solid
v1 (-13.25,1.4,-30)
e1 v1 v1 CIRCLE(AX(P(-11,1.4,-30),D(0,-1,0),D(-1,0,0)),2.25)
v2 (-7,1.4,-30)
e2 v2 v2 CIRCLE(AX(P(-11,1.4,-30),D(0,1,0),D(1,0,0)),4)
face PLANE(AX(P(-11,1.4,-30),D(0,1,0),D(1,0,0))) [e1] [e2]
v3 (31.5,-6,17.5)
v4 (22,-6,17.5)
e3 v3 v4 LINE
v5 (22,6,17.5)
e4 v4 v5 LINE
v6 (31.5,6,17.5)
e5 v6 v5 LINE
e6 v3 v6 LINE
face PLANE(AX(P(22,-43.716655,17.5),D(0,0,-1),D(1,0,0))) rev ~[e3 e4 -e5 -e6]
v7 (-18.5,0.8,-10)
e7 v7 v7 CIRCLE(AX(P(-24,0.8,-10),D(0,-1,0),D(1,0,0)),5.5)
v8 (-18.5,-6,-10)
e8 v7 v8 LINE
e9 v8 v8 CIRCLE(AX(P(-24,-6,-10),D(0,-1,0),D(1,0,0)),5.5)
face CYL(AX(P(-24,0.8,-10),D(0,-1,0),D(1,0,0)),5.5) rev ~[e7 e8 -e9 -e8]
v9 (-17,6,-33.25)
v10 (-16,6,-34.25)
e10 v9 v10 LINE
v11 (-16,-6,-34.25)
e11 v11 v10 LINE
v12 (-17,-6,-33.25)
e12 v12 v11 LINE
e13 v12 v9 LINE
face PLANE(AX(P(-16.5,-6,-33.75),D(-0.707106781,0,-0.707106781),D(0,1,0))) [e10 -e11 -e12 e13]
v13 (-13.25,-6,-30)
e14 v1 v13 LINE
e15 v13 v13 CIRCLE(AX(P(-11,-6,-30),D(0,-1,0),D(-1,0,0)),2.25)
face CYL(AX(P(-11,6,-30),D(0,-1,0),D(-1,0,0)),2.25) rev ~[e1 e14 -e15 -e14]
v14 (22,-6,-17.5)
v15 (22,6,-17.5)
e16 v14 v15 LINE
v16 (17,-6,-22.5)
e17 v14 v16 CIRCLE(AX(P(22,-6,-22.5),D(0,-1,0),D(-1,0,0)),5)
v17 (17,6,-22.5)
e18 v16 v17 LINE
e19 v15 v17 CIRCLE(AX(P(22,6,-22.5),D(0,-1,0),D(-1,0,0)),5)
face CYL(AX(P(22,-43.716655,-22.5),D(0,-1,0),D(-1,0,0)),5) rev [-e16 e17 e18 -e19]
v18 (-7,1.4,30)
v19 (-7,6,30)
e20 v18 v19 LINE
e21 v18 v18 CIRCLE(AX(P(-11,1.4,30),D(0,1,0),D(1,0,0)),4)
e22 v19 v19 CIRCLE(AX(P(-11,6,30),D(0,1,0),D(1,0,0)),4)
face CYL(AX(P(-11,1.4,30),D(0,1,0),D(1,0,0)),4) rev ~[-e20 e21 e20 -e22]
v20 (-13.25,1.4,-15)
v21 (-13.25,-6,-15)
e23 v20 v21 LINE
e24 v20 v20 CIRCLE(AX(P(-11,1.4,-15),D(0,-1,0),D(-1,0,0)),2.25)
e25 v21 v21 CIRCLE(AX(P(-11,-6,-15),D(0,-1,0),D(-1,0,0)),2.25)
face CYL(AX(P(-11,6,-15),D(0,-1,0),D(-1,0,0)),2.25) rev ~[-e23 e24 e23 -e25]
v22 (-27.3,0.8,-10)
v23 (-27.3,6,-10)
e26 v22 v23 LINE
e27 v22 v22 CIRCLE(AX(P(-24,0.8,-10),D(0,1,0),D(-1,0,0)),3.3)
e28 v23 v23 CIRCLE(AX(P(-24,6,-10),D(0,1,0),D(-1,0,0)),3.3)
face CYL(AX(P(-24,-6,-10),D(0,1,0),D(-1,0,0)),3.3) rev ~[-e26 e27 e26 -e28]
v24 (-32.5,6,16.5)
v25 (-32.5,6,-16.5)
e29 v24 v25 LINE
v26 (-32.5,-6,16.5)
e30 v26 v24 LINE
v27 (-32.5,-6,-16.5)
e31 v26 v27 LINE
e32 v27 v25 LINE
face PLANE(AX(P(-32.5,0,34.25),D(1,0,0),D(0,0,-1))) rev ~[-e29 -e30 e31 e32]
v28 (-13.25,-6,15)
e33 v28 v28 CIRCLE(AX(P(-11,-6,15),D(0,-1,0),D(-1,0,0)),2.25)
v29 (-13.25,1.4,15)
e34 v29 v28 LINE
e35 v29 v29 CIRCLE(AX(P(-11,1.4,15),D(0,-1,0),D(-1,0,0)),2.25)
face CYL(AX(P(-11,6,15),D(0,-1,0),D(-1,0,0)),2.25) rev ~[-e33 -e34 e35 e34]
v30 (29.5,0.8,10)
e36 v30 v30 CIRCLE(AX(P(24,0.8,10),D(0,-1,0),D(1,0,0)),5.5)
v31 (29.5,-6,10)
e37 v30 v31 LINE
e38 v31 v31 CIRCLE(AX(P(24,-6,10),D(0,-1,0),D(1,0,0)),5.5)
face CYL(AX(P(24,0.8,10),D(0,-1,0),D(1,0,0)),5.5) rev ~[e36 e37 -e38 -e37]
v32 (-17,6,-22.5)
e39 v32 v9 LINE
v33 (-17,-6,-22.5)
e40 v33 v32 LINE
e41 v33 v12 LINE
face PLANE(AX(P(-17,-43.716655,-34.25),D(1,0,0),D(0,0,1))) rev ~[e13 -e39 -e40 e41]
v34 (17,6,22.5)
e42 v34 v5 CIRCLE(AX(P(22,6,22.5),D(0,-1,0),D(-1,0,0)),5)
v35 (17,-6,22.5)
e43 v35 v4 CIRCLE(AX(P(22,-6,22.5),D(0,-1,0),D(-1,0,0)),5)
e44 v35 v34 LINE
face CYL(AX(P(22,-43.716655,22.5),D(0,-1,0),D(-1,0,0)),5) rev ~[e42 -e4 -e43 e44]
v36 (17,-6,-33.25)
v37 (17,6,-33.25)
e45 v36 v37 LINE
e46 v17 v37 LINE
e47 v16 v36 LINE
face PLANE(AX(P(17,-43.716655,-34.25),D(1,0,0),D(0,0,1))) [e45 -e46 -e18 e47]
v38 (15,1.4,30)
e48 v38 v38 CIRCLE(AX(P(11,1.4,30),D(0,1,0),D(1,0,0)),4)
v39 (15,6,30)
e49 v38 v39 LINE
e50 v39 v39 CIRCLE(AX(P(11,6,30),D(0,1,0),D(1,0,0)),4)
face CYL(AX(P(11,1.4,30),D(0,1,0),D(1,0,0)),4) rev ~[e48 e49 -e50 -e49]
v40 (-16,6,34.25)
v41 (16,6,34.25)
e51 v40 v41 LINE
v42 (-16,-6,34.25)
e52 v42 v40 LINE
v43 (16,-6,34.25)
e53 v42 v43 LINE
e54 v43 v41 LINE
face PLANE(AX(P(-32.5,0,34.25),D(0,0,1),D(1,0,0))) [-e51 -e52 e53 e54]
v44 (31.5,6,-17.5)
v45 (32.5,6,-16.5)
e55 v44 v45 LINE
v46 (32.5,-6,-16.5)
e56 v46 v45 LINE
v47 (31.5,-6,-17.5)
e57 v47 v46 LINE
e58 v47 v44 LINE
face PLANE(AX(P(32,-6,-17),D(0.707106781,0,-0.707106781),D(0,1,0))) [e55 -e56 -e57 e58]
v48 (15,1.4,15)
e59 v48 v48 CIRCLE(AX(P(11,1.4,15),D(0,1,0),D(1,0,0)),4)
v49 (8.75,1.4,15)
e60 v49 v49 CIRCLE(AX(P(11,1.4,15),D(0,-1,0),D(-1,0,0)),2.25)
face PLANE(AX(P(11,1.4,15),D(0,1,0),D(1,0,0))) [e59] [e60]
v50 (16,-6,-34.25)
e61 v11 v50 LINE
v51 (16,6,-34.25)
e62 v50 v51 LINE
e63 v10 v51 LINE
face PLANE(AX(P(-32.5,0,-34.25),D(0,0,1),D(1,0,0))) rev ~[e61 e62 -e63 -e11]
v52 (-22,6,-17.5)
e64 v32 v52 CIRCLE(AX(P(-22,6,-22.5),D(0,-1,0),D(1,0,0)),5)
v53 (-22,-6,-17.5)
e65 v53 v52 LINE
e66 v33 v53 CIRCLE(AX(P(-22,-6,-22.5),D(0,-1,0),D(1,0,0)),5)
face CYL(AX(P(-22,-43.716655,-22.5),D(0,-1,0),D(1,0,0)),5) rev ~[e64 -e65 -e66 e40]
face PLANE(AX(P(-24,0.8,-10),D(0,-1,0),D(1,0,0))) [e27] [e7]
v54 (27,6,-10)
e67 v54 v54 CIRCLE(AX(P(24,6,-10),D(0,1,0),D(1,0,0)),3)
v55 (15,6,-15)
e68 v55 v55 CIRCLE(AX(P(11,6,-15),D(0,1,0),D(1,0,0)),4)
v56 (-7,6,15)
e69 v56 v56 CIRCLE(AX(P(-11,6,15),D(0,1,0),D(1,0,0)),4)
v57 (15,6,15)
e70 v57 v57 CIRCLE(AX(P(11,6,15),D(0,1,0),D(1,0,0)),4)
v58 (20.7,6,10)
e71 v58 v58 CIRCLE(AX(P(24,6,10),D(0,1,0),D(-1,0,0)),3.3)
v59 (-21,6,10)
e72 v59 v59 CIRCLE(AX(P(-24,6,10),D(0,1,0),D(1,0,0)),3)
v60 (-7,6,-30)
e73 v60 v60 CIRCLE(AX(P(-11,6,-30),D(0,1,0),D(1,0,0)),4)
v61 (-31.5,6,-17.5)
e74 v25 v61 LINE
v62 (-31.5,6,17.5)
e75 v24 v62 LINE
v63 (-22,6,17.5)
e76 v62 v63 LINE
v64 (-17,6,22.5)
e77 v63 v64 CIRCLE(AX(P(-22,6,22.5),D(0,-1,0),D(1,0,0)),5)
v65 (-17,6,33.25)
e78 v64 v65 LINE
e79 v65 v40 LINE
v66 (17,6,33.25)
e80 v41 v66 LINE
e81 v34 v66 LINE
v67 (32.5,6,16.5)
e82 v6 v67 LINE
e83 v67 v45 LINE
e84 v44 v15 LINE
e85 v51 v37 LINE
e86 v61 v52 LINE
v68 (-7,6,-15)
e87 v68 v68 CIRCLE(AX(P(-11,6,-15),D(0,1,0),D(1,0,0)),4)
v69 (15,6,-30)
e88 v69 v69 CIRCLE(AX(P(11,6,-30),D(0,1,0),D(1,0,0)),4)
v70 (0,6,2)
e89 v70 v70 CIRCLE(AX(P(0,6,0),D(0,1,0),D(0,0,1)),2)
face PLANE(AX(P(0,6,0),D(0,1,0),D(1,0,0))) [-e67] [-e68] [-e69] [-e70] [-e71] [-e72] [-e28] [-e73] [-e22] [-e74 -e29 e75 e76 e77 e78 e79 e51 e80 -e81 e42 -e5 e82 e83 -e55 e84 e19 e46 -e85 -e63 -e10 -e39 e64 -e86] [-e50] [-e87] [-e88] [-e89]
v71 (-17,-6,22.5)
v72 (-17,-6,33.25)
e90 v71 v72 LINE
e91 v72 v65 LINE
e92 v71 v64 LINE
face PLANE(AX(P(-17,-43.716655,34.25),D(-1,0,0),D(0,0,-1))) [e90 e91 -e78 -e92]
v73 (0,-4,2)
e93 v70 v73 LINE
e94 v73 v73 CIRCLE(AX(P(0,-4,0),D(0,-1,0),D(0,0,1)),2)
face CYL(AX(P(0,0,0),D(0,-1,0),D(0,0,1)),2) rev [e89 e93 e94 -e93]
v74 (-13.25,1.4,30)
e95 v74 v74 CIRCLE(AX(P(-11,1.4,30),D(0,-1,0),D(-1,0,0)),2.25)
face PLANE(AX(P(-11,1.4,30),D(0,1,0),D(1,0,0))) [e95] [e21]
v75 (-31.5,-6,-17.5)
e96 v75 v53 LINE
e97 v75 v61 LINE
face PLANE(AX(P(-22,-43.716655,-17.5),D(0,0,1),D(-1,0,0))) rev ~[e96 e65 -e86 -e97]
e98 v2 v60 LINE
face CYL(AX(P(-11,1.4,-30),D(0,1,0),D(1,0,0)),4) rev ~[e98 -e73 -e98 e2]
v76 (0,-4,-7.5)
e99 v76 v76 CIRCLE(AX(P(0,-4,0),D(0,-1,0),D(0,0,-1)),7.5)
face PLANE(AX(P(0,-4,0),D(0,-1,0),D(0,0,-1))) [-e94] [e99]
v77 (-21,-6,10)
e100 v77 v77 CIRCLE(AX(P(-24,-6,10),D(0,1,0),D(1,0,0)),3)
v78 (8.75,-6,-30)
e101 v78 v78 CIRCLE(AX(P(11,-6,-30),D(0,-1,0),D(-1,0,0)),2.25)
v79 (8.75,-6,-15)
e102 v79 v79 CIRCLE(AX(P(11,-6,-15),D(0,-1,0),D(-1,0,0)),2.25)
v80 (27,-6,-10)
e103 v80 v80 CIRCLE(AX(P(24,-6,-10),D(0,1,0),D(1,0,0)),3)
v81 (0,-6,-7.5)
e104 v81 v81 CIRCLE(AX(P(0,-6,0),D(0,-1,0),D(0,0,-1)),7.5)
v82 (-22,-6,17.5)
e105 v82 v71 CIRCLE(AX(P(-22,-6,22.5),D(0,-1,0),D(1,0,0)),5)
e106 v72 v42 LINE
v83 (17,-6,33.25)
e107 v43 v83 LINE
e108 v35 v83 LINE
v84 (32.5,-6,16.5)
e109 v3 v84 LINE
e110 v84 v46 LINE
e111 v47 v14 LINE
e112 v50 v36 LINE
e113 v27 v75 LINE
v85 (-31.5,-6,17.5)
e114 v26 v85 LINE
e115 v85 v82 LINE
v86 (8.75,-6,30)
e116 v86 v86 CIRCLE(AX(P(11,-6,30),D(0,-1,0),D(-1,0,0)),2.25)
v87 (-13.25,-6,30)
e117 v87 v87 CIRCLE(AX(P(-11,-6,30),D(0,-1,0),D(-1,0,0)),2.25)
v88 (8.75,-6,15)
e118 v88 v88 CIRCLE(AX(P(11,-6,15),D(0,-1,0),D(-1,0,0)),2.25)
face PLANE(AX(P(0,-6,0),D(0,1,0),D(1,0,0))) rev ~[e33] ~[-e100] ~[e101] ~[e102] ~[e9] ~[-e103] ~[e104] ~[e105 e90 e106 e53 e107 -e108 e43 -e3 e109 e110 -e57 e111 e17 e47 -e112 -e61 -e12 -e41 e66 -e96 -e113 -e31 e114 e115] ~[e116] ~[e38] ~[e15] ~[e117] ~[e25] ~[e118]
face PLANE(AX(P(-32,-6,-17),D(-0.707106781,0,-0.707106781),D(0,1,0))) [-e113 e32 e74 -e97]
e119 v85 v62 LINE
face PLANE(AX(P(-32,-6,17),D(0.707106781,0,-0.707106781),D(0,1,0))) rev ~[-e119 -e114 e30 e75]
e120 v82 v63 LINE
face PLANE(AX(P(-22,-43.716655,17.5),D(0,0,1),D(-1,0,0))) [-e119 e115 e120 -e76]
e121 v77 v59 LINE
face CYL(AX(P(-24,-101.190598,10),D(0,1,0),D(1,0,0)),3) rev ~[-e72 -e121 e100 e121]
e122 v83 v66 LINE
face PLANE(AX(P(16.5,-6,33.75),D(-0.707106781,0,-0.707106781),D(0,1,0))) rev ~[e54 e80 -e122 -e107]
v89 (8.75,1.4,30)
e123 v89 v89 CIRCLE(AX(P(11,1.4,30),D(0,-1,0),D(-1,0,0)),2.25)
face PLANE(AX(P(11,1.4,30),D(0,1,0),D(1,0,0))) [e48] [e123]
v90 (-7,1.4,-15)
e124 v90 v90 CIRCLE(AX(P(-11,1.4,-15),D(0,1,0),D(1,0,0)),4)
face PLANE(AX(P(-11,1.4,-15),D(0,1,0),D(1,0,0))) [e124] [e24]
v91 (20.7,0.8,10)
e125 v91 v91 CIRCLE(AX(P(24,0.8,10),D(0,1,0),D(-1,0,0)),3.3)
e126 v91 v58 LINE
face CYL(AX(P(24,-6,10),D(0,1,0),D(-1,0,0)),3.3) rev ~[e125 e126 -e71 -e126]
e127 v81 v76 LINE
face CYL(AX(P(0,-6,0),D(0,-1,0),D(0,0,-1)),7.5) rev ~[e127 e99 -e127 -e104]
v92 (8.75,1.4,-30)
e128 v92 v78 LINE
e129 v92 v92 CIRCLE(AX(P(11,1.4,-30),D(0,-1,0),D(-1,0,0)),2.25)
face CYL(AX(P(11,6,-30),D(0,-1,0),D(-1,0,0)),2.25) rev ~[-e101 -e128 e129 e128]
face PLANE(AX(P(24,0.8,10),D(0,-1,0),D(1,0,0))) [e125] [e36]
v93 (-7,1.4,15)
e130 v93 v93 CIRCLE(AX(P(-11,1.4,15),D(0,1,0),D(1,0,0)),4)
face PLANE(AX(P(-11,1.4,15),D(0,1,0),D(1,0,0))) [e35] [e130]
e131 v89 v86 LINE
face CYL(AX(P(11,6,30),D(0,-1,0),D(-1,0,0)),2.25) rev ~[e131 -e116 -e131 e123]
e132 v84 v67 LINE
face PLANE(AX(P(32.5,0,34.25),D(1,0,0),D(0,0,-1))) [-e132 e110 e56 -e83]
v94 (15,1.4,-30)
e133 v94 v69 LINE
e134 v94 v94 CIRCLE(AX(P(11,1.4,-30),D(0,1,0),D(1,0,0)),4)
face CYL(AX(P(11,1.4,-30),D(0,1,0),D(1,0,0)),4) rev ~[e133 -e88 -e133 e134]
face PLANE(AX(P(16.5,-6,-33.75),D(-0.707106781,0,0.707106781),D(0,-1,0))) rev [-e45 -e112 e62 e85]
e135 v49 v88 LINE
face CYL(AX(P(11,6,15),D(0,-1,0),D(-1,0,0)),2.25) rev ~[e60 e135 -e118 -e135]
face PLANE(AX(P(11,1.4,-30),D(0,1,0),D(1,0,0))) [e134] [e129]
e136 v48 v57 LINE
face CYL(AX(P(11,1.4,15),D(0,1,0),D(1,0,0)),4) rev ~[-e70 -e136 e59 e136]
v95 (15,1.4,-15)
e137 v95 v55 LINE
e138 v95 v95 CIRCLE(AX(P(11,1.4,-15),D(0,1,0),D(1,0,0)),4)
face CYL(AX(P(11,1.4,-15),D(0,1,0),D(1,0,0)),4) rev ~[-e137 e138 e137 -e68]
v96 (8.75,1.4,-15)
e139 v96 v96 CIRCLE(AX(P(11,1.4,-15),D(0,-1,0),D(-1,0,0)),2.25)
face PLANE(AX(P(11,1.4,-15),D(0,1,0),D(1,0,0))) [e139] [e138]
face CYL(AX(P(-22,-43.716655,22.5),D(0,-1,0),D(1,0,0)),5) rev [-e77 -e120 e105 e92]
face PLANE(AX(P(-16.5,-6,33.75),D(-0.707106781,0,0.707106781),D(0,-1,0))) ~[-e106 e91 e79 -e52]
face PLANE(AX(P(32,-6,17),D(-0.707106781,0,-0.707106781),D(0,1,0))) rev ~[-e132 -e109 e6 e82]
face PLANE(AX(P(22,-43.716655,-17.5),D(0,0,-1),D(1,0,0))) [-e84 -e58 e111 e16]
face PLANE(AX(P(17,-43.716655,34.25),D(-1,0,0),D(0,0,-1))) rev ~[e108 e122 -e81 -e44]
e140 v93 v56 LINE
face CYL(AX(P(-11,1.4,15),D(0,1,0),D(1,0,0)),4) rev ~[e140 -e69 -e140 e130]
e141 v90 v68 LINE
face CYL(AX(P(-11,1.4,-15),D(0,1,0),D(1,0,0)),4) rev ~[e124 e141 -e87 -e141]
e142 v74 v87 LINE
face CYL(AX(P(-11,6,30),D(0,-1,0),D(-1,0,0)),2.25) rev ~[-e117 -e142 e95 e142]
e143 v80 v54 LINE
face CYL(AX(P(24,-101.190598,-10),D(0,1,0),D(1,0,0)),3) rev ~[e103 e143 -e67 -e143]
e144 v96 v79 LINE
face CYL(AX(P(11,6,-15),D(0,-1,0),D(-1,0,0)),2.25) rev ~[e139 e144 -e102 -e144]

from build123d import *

# Parameters (mm, degrees)
SKETCH_1_W                   = 65
SKETCH_1_H                   = 68.5
SKETCH_1_R                   = 2
EXTRUDE_1_DEPTH              = 6
HOLE_WIZARD_M6_1_D           = 6.6
HOLE_WIZARD_M6_1_CBORE_D     = 11
HOLE_WIZARD_M6_1_CBORE_DEPTH = 6.8
HOLE_WIZARD_M4_1_D           = 4.5
HOLE_WIZARD_M4_1_CBORE_D     = 8
HOLE_WIZARD_M4_1_CBORE_DEPTH = 4.6
CUT_EXTRUDE_1_DEPTH          = 49.716655263
CUT_EXTRUDE_1_DEPTH_BACK     = 49.716655263
F_6_0MM_1_D                  = 6
CHAMFER_1_SIZE               = 1
SKETCH_9_R                   = 7.5
CUT_EXTRUDE_2_DEPTH          = 2


with BuildPart() as part:
    # 草图1 → 凸台-拉伸1 (new, symmetric)
    with BuildSketch(Plane(origin=(0, 0, 0), x_dir=(1, 0, 0), z_dir=(0, 1, 0))):
        Rectangle(SKETCH_1_W, SKETCH_1_H)
        with Locations(Location((0, 0, 0), (0, 0, 270))):
            Circle(SKETCH_1_R, mode=Mode.SUBTRACT)
    extrude(amount=EXTRUDE_1_DEPTH, both=True)

    # M6 六角圆柱头螺钉的柱形沉头孔1 (through all)
    with Locations(Plane.XZ.offset(6)):
        with Locations((-24, -10), (24, 10)):
            CounterBoreHole(HOLE_WIZARD_M6_1_D / 2, HOLE_WIZARD_M6_1_CBORE_D / 2, HOLE_WIZARD_M6_1_CBORE_DEPTH)

    # M4 六角圆柱头螺钉的柱形沉头孔1 (through all)
    with Locations(Plane(origin=(0, 6, 0), x_dir=(1, 0, 0), z_dir=(0, 1, 0))):
        with Locations((-11, -15), (-11, -30), (11, -30), (11, -15), (11, 15), (11, 30), (-11, 30), (-11, 15)):
            CounterBoreHole(HOLE_WIZARD_M4_1_D / 2, HOLE_WIZARD_M4_1_CBORE_D / 2, HOLE_WIZARD_M4_1_CBORE_DEPTH)

    # 草图6 → 切除-拉伸1 (cut, two sides: drawn at the far end of the back side and taken through both)
    with BuildSketch(Plane(origin=(0, 6, 0), x_dir=(1, 0, 0), z_dir=(0, 1, 0)).offset(-CUT_EXTRUDE_1_DEPTH_BACK)):
        with BuildLine():
            Line((-32.5, 34.25), (-17, 34.25))
            Line((-17, 34.25), (-17, 22.5))
            ThreePointArc((-17, 22.5), (-18.464466094, 18.964466094), (-22, 17.5))
            Line((-22, 17.5), (-32.5, 17.5))
            Line((-32.5, 17.5), (-32.5, 34.25))
        make_face()
        with BuildLine():
            Line((-17, -34.25), (-17, -22.5))
            ThreePointArc((-17, -22.5), (-18.464466094, -18.964466094), (-22, -17.5))
            Line((-22, -17.5), (-32.5, -17.5))
            Line((-32.5, -17.5), (-32.5, -34.25))
            Line((-32.5, -34.25), (-17, -34.25))
        make_face()
        with BuildLine():
            Line((32.5, -34.25), (17, -34.25))
            Line((17, -34.25), (17, -22.5))
            ThreePointArc((17, -22.5), (18.464466094, -18.964466094), (22, -17.5))
            Line((22, -17.5), (32.5, -17.5))
            Line((32.5, -17.5), (32.5, -34.25))
        make_face()
        with BuildLine():
            Line((17, 34.25), (17, 22.5))
            ThreePointArc((17, 22.5), (18.464466094, 18.964466094), (22, 17.5))
            Line((22, 17.5), (32.5, 17.5))
            Line((32.5, 17.5), (32.5, 34.25))
            Line((32.5, 34.25), (17, 34.25))
        make_face()
    extrude(amount=CUT_EXTRUDE_1_DEPTH + CUT_EXTRUDE_1_DEPTH_BACK, mode=Mode.SUBTRACT)

    # Ø6.0mm 暗销孔1 (through all)
    with Locations(Plane(origin=(0, -6, 0), x_dir=(-1, 0, 0), z_dir=(0, -1, 0))):
        with Locations((-24, 10), (24, -10)):
            Hole(F_6_0MM_1_D / 2)

    # 倒角1
    chamfer_1_edges = [part.edges().sort_by_distance(p)[0] for p in [
        (0, -6, -2),
        (17, 0, -34.25),
        (32.5, 0, -17.5),
        (32.5, 0, 17.5),
        (17, 0, 34.25),
        (-17, 0, 34.25),
        (-32.5, 0, 17.5),
        (-32.5, 0, -17.5),
        (-17, 0, -34.25),
    ]]
    chamfer(chamfer_1_edges, length=CHAMFER_1_SIZE)

    # 草图9 → 切除-拉伸2 (cut)
    with BuildSketch(Plane.XZ.offset(6)):
        with Locations(Location((0, 0, 0), (0, 0, 270))):
            Circle(SKETCH_9_R)
    extrude(amount=-CUT_EXTRUDE_2_DEPTH, mode=Mode.SUBTRACT)


solid = part.part
